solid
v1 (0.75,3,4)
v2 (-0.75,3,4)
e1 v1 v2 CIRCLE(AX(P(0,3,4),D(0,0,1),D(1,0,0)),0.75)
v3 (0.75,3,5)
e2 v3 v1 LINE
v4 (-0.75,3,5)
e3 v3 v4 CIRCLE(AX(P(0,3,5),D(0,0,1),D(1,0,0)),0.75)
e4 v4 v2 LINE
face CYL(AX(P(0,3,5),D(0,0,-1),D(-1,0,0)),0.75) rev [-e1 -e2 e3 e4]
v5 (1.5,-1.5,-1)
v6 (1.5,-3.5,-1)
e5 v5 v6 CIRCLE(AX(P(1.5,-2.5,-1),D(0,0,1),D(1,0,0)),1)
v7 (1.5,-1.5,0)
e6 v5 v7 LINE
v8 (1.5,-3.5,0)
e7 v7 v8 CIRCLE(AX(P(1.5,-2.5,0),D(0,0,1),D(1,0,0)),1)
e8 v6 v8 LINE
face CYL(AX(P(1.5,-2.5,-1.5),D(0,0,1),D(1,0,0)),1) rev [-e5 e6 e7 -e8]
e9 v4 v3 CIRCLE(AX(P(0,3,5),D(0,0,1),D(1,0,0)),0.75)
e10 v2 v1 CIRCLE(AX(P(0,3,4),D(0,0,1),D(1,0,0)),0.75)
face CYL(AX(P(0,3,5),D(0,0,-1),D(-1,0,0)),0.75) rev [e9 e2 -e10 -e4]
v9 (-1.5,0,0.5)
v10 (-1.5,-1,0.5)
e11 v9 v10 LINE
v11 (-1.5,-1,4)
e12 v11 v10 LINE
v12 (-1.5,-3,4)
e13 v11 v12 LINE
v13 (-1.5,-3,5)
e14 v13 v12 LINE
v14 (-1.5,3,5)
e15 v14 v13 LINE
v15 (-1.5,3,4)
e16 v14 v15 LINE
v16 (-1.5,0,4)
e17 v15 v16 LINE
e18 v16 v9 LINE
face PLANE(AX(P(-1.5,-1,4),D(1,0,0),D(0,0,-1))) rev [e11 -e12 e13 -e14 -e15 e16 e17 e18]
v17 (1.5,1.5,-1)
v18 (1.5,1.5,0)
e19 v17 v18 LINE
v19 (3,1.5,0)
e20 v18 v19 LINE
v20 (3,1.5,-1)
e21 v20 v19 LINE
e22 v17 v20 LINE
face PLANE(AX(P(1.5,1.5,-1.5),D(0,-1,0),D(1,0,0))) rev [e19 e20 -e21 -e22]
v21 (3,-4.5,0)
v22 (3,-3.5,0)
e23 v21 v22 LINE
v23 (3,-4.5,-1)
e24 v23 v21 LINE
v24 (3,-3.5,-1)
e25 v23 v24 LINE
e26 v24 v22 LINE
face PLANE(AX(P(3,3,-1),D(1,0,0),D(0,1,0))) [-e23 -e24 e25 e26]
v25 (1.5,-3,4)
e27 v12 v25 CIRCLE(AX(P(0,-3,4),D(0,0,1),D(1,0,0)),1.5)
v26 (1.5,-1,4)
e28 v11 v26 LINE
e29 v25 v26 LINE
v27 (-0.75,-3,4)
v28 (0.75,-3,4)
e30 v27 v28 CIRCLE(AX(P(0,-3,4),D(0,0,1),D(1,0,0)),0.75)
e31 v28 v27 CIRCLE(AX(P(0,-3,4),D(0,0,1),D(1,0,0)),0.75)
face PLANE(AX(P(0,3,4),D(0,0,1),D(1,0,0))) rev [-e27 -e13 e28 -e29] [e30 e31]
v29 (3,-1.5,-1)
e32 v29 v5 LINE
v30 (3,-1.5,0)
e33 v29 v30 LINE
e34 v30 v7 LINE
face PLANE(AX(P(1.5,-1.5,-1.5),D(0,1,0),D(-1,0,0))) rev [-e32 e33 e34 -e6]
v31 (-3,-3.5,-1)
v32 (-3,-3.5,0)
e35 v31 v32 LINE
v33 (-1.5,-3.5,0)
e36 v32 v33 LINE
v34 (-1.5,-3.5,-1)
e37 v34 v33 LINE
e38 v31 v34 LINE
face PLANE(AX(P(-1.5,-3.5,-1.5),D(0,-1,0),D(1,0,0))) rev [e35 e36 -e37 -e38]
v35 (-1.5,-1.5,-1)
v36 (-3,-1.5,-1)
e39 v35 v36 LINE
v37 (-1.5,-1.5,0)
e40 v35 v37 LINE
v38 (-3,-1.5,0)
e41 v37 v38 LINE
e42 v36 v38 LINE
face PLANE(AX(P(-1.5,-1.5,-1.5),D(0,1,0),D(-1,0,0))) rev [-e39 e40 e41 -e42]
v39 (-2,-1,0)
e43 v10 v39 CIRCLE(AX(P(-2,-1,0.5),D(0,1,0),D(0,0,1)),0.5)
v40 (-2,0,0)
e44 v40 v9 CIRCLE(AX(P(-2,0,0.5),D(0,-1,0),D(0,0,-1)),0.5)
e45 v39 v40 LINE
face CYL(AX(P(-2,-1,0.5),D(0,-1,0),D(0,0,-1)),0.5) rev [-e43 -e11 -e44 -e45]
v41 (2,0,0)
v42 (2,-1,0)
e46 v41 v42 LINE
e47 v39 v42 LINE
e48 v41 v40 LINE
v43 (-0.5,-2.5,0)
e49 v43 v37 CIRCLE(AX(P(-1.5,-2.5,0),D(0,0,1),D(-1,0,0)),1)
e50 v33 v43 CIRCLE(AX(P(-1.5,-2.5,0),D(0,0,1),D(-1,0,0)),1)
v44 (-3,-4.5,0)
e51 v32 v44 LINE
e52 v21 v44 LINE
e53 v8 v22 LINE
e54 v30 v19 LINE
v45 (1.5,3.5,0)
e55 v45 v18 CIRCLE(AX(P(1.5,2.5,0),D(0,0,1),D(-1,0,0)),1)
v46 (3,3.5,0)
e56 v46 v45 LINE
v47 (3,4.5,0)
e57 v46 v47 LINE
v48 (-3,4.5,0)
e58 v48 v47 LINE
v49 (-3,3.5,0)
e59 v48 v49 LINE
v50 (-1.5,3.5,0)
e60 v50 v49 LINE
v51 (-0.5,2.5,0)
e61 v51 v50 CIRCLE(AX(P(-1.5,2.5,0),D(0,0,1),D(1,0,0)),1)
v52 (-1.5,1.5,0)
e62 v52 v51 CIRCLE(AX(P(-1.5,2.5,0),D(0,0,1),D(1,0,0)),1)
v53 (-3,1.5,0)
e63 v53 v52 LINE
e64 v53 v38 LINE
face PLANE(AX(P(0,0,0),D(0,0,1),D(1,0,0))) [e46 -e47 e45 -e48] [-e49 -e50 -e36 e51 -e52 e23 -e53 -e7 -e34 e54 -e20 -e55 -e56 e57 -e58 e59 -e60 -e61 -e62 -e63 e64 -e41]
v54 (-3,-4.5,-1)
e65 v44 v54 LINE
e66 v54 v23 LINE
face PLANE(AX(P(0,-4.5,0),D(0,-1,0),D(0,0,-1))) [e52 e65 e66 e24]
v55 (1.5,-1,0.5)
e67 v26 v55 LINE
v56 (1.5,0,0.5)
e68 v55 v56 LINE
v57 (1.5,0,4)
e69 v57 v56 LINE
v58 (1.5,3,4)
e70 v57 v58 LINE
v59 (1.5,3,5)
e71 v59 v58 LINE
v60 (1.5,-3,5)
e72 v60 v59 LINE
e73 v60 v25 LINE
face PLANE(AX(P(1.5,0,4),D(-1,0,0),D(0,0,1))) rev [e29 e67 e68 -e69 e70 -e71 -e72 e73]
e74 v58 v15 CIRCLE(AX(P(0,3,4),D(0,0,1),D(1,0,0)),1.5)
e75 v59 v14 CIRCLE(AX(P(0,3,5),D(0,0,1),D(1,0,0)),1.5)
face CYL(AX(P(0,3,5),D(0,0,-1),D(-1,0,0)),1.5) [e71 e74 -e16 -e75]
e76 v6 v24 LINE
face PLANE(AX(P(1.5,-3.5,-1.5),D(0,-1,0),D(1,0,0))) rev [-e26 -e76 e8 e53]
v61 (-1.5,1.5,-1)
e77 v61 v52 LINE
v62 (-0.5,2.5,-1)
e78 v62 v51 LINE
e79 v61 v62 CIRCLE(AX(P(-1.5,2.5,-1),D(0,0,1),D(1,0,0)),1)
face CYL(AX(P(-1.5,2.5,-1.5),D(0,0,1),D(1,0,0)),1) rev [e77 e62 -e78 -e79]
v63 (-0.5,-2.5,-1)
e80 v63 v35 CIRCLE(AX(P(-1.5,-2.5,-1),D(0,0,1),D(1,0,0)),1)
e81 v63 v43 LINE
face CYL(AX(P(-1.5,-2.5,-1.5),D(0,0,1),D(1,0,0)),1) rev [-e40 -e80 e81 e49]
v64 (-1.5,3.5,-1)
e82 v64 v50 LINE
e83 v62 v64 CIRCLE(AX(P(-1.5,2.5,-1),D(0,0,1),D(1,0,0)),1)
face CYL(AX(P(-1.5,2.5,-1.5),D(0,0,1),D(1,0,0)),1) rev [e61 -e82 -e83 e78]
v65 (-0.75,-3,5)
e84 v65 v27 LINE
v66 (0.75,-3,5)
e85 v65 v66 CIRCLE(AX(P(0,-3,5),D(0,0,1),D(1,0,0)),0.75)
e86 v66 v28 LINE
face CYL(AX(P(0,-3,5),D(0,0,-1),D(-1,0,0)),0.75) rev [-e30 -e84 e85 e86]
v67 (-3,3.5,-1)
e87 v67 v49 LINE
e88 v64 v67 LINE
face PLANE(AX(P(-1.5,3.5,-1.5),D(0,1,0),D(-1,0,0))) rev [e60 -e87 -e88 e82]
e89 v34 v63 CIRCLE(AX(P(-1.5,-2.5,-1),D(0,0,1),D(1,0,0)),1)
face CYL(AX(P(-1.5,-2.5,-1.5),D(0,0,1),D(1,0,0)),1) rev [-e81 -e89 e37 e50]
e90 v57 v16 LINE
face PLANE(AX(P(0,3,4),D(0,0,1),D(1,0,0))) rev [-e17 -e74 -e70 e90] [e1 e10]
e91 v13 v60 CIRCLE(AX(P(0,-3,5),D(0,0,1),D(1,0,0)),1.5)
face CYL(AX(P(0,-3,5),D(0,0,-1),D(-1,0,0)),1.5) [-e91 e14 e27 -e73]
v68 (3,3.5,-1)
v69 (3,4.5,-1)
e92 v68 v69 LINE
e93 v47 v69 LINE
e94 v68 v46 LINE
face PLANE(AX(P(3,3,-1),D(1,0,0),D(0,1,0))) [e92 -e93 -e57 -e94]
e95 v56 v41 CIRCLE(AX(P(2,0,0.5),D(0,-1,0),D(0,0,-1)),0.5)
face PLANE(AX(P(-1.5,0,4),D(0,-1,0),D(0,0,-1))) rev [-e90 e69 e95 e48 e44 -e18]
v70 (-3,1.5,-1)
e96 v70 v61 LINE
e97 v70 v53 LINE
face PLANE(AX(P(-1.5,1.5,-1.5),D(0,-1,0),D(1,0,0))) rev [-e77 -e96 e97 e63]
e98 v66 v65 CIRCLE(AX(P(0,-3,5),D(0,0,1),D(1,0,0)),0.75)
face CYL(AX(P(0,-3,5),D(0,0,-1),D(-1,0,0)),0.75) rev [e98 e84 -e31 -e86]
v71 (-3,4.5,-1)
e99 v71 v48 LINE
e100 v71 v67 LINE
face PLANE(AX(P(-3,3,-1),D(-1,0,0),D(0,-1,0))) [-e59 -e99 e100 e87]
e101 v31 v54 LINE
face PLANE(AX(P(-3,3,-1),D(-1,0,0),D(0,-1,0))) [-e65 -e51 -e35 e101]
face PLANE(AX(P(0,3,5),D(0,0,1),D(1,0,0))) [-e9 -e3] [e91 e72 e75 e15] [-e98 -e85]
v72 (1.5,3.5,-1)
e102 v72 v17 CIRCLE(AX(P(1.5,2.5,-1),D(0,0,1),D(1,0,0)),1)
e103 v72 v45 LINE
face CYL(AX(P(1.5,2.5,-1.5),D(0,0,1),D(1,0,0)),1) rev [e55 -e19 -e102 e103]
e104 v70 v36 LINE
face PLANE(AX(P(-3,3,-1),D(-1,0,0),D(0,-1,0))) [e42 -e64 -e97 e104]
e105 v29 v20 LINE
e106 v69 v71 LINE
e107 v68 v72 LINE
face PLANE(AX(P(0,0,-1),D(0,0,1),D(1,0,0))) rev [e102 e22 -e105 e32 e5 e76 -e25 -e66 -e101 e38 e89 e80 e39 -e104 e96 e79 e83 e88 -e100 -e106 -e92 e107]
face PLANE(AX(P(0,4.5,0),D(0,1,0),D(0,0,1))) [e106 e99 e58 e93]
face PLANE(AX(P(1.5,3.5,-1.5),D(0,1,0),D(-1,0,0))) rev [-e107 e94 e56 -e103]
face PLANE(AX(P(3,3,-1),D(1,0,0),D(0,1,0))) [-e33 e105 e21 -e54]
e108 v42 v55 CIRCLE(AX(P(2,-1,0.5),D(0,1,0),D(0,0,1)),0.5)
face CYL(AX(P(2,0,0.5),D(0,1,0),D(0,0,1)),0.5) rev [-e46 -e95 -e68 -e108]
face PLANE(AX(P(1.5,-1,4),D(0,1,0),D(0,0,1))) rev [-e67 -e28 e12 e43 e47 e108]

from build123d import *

# Parameters (mm, degrees)
BASE_PLATE_SKETCH_W  = 6
BASE_PLATE_SKETCH_H  = 6
BASE_PLATE_DEPTH     = 1
UPPER_PAD_SKETCH_W   = 6
UPPER_PAD_SKETCH_H   = 1
UPPER_PAD_DEPTH      = 1.5
LOWER_PAD_SKETCH_W   = 6
LOWER_PAD_SKETCH_H   = 1
LOWER_PAD_DEPTH      = 1.5
NOTCH_CUTS_DEPTH     = 1.5
STEM_SKETCH_W        = 3
STEM_SKETCH_H        = 1
STEM_1X3_DEPTH       = 4
STEM_FILLET_R0_5_A_R = 0.5
STEM_FILLET_R0_5_B_R = 0.5
LUG_PLATE_SKETCH_R   = 0.75
LUG_PLATE_DEPTH      = 1


with BuildPart() as part:
    # Base Plate Sketch → Base Plate (new body)
    with BuildSketch(Plane.XY):
        Rectangle(BASE_PLATE_SKETCH_W, BASE_PLATE_SKETCH_H)
    extrude(amount=-BASE_PLATE_DEPTH)

    # Upper Pad Sketch → Upper Pad (add)
    with BuildSketch(Plane(origin=(0, 3, 0), x_dir=(1, 0, 0), z_dir=(0, 1, 0))):
        with Locations((0, 0.5)):
            Rectangle(UPPER_PAD_SKETCH_W, UPPER_PAD_SKETCH_H)
    extrude(amount=UPPER_PAD_DEPTH)

    # Lower Pad Sketch → Lower Pad (add)
    with BuildSketch(Plane.XZ.offset(3)):
        with Locations((0, -0.5)):
            Rectangle(LOWER_PAD_SKETCH_W, LOWER_PAD_SKETCH_H)
    extrude(amount=LOWER_PAD_DEPTH)

    # Notch Cut Sketch → Notch Cuts (cut)
    with BuildSketch(Plane.XY):
        with BuildLine():
            Line((-1.5, 3.5), (-3, 3.5))
            Line((-3, 3.5), (-3, 1.5))
            Line((-3, 1.5), (-1.5, 1.5))
            ThreePointArc((-1.5, 1.5), (-0.5, 2.5), (-1.5, 3.5))
        make_face()
        with BuildLine():
            Line((1.5, 3.5), (3, 3.5))
            Line((3, 3.5), (3, 1.5))
            Line((3, 1.5), (1.5, 1.5))
            ThreePointArc((1.5, 1.5), (0.5, 2.5), (1.5, 3.5))
        make_face()
        with BuildLine():
            Line((3, -1.5), (3, -3.5))
            Line((3, -3.5), (1.5, -3.5))
            ThreePointArc((1.5, -3.5), (0.5, -2.5), (1.5, -1.5))
            Line((1.5, -1.5), (3, -1.5))
        make_face()
        with BuildLine():
            Line((-1.5, -1.5), (-3, -1.5))
            Line((-3, -1.5), (-3, -3.5))
            Line((-3, -3.5), (-1.5, -3.5))
            ThreePointArc((-1.5, -3.5), (-0.5, -2.5), (-1.5, -1.5))
        make_face()
    extrude(amount=-NOTCH_CUTS_DEPTH, mode=Mode.SUBTRACT)

    # Stem Sketch → Stem 1x3 (add)
    with BuildSketch(Plane.XY):
        with Locations((0, -0.5)):
            Rectangle(STEM_SKETCH_W, STEM_SKETCH_H)
    extrude(amount=STEM_1X3_DEPTH)

    # Stem Fillet R0.5 A
    stem_fillet_r0_5_a_edges = [part.edges().sort_by_distance(p)[0] for p in [
        (1.5, -0.5, 0),
    ]]
    fillet(stem_fillet_r0_5_a_edges, radius=STEM_FILLET_R0_5_A_R)

    # Stem Fillet R0.5 B
    stem_fillet_r0_5_b_edges = [part.edges().sort_by_distance(p)[0] for p in [
        (-1.5, -0.5, 0),
    ]]
    fillet(stem_fillet_r0_5_b_edges, radius=STEM_FILLET_R0_5_B_R)

    # Lug Plate Sketch → Lug Plate (add)
    with BuildSketch(Plane.XY.offset(4)):
        with BuildLine():
            Line((1.5, 3), (1.5, -3))
            ThreePointArc((1.5, -3), (0, -4.5), (-1.5, -3))
            Line((-1.5, -3), (-1.5, 3))
            ThreePointArc((-1.5, 3), (0, 4.5), (1.5, 3))
        make_face()
        with Locations((0, 3)):
            Circle(LUG_PLATE_SKETCH_R, mode=Mode.SUBTRACT)
        with Locations((0, -3)):
            Circle(LUG_PLATE_SKETCH_R, mode=Mode.SUBTRACT)
    extrude(amount=LUG_PLATE_DEPTH)


solid = part.part
